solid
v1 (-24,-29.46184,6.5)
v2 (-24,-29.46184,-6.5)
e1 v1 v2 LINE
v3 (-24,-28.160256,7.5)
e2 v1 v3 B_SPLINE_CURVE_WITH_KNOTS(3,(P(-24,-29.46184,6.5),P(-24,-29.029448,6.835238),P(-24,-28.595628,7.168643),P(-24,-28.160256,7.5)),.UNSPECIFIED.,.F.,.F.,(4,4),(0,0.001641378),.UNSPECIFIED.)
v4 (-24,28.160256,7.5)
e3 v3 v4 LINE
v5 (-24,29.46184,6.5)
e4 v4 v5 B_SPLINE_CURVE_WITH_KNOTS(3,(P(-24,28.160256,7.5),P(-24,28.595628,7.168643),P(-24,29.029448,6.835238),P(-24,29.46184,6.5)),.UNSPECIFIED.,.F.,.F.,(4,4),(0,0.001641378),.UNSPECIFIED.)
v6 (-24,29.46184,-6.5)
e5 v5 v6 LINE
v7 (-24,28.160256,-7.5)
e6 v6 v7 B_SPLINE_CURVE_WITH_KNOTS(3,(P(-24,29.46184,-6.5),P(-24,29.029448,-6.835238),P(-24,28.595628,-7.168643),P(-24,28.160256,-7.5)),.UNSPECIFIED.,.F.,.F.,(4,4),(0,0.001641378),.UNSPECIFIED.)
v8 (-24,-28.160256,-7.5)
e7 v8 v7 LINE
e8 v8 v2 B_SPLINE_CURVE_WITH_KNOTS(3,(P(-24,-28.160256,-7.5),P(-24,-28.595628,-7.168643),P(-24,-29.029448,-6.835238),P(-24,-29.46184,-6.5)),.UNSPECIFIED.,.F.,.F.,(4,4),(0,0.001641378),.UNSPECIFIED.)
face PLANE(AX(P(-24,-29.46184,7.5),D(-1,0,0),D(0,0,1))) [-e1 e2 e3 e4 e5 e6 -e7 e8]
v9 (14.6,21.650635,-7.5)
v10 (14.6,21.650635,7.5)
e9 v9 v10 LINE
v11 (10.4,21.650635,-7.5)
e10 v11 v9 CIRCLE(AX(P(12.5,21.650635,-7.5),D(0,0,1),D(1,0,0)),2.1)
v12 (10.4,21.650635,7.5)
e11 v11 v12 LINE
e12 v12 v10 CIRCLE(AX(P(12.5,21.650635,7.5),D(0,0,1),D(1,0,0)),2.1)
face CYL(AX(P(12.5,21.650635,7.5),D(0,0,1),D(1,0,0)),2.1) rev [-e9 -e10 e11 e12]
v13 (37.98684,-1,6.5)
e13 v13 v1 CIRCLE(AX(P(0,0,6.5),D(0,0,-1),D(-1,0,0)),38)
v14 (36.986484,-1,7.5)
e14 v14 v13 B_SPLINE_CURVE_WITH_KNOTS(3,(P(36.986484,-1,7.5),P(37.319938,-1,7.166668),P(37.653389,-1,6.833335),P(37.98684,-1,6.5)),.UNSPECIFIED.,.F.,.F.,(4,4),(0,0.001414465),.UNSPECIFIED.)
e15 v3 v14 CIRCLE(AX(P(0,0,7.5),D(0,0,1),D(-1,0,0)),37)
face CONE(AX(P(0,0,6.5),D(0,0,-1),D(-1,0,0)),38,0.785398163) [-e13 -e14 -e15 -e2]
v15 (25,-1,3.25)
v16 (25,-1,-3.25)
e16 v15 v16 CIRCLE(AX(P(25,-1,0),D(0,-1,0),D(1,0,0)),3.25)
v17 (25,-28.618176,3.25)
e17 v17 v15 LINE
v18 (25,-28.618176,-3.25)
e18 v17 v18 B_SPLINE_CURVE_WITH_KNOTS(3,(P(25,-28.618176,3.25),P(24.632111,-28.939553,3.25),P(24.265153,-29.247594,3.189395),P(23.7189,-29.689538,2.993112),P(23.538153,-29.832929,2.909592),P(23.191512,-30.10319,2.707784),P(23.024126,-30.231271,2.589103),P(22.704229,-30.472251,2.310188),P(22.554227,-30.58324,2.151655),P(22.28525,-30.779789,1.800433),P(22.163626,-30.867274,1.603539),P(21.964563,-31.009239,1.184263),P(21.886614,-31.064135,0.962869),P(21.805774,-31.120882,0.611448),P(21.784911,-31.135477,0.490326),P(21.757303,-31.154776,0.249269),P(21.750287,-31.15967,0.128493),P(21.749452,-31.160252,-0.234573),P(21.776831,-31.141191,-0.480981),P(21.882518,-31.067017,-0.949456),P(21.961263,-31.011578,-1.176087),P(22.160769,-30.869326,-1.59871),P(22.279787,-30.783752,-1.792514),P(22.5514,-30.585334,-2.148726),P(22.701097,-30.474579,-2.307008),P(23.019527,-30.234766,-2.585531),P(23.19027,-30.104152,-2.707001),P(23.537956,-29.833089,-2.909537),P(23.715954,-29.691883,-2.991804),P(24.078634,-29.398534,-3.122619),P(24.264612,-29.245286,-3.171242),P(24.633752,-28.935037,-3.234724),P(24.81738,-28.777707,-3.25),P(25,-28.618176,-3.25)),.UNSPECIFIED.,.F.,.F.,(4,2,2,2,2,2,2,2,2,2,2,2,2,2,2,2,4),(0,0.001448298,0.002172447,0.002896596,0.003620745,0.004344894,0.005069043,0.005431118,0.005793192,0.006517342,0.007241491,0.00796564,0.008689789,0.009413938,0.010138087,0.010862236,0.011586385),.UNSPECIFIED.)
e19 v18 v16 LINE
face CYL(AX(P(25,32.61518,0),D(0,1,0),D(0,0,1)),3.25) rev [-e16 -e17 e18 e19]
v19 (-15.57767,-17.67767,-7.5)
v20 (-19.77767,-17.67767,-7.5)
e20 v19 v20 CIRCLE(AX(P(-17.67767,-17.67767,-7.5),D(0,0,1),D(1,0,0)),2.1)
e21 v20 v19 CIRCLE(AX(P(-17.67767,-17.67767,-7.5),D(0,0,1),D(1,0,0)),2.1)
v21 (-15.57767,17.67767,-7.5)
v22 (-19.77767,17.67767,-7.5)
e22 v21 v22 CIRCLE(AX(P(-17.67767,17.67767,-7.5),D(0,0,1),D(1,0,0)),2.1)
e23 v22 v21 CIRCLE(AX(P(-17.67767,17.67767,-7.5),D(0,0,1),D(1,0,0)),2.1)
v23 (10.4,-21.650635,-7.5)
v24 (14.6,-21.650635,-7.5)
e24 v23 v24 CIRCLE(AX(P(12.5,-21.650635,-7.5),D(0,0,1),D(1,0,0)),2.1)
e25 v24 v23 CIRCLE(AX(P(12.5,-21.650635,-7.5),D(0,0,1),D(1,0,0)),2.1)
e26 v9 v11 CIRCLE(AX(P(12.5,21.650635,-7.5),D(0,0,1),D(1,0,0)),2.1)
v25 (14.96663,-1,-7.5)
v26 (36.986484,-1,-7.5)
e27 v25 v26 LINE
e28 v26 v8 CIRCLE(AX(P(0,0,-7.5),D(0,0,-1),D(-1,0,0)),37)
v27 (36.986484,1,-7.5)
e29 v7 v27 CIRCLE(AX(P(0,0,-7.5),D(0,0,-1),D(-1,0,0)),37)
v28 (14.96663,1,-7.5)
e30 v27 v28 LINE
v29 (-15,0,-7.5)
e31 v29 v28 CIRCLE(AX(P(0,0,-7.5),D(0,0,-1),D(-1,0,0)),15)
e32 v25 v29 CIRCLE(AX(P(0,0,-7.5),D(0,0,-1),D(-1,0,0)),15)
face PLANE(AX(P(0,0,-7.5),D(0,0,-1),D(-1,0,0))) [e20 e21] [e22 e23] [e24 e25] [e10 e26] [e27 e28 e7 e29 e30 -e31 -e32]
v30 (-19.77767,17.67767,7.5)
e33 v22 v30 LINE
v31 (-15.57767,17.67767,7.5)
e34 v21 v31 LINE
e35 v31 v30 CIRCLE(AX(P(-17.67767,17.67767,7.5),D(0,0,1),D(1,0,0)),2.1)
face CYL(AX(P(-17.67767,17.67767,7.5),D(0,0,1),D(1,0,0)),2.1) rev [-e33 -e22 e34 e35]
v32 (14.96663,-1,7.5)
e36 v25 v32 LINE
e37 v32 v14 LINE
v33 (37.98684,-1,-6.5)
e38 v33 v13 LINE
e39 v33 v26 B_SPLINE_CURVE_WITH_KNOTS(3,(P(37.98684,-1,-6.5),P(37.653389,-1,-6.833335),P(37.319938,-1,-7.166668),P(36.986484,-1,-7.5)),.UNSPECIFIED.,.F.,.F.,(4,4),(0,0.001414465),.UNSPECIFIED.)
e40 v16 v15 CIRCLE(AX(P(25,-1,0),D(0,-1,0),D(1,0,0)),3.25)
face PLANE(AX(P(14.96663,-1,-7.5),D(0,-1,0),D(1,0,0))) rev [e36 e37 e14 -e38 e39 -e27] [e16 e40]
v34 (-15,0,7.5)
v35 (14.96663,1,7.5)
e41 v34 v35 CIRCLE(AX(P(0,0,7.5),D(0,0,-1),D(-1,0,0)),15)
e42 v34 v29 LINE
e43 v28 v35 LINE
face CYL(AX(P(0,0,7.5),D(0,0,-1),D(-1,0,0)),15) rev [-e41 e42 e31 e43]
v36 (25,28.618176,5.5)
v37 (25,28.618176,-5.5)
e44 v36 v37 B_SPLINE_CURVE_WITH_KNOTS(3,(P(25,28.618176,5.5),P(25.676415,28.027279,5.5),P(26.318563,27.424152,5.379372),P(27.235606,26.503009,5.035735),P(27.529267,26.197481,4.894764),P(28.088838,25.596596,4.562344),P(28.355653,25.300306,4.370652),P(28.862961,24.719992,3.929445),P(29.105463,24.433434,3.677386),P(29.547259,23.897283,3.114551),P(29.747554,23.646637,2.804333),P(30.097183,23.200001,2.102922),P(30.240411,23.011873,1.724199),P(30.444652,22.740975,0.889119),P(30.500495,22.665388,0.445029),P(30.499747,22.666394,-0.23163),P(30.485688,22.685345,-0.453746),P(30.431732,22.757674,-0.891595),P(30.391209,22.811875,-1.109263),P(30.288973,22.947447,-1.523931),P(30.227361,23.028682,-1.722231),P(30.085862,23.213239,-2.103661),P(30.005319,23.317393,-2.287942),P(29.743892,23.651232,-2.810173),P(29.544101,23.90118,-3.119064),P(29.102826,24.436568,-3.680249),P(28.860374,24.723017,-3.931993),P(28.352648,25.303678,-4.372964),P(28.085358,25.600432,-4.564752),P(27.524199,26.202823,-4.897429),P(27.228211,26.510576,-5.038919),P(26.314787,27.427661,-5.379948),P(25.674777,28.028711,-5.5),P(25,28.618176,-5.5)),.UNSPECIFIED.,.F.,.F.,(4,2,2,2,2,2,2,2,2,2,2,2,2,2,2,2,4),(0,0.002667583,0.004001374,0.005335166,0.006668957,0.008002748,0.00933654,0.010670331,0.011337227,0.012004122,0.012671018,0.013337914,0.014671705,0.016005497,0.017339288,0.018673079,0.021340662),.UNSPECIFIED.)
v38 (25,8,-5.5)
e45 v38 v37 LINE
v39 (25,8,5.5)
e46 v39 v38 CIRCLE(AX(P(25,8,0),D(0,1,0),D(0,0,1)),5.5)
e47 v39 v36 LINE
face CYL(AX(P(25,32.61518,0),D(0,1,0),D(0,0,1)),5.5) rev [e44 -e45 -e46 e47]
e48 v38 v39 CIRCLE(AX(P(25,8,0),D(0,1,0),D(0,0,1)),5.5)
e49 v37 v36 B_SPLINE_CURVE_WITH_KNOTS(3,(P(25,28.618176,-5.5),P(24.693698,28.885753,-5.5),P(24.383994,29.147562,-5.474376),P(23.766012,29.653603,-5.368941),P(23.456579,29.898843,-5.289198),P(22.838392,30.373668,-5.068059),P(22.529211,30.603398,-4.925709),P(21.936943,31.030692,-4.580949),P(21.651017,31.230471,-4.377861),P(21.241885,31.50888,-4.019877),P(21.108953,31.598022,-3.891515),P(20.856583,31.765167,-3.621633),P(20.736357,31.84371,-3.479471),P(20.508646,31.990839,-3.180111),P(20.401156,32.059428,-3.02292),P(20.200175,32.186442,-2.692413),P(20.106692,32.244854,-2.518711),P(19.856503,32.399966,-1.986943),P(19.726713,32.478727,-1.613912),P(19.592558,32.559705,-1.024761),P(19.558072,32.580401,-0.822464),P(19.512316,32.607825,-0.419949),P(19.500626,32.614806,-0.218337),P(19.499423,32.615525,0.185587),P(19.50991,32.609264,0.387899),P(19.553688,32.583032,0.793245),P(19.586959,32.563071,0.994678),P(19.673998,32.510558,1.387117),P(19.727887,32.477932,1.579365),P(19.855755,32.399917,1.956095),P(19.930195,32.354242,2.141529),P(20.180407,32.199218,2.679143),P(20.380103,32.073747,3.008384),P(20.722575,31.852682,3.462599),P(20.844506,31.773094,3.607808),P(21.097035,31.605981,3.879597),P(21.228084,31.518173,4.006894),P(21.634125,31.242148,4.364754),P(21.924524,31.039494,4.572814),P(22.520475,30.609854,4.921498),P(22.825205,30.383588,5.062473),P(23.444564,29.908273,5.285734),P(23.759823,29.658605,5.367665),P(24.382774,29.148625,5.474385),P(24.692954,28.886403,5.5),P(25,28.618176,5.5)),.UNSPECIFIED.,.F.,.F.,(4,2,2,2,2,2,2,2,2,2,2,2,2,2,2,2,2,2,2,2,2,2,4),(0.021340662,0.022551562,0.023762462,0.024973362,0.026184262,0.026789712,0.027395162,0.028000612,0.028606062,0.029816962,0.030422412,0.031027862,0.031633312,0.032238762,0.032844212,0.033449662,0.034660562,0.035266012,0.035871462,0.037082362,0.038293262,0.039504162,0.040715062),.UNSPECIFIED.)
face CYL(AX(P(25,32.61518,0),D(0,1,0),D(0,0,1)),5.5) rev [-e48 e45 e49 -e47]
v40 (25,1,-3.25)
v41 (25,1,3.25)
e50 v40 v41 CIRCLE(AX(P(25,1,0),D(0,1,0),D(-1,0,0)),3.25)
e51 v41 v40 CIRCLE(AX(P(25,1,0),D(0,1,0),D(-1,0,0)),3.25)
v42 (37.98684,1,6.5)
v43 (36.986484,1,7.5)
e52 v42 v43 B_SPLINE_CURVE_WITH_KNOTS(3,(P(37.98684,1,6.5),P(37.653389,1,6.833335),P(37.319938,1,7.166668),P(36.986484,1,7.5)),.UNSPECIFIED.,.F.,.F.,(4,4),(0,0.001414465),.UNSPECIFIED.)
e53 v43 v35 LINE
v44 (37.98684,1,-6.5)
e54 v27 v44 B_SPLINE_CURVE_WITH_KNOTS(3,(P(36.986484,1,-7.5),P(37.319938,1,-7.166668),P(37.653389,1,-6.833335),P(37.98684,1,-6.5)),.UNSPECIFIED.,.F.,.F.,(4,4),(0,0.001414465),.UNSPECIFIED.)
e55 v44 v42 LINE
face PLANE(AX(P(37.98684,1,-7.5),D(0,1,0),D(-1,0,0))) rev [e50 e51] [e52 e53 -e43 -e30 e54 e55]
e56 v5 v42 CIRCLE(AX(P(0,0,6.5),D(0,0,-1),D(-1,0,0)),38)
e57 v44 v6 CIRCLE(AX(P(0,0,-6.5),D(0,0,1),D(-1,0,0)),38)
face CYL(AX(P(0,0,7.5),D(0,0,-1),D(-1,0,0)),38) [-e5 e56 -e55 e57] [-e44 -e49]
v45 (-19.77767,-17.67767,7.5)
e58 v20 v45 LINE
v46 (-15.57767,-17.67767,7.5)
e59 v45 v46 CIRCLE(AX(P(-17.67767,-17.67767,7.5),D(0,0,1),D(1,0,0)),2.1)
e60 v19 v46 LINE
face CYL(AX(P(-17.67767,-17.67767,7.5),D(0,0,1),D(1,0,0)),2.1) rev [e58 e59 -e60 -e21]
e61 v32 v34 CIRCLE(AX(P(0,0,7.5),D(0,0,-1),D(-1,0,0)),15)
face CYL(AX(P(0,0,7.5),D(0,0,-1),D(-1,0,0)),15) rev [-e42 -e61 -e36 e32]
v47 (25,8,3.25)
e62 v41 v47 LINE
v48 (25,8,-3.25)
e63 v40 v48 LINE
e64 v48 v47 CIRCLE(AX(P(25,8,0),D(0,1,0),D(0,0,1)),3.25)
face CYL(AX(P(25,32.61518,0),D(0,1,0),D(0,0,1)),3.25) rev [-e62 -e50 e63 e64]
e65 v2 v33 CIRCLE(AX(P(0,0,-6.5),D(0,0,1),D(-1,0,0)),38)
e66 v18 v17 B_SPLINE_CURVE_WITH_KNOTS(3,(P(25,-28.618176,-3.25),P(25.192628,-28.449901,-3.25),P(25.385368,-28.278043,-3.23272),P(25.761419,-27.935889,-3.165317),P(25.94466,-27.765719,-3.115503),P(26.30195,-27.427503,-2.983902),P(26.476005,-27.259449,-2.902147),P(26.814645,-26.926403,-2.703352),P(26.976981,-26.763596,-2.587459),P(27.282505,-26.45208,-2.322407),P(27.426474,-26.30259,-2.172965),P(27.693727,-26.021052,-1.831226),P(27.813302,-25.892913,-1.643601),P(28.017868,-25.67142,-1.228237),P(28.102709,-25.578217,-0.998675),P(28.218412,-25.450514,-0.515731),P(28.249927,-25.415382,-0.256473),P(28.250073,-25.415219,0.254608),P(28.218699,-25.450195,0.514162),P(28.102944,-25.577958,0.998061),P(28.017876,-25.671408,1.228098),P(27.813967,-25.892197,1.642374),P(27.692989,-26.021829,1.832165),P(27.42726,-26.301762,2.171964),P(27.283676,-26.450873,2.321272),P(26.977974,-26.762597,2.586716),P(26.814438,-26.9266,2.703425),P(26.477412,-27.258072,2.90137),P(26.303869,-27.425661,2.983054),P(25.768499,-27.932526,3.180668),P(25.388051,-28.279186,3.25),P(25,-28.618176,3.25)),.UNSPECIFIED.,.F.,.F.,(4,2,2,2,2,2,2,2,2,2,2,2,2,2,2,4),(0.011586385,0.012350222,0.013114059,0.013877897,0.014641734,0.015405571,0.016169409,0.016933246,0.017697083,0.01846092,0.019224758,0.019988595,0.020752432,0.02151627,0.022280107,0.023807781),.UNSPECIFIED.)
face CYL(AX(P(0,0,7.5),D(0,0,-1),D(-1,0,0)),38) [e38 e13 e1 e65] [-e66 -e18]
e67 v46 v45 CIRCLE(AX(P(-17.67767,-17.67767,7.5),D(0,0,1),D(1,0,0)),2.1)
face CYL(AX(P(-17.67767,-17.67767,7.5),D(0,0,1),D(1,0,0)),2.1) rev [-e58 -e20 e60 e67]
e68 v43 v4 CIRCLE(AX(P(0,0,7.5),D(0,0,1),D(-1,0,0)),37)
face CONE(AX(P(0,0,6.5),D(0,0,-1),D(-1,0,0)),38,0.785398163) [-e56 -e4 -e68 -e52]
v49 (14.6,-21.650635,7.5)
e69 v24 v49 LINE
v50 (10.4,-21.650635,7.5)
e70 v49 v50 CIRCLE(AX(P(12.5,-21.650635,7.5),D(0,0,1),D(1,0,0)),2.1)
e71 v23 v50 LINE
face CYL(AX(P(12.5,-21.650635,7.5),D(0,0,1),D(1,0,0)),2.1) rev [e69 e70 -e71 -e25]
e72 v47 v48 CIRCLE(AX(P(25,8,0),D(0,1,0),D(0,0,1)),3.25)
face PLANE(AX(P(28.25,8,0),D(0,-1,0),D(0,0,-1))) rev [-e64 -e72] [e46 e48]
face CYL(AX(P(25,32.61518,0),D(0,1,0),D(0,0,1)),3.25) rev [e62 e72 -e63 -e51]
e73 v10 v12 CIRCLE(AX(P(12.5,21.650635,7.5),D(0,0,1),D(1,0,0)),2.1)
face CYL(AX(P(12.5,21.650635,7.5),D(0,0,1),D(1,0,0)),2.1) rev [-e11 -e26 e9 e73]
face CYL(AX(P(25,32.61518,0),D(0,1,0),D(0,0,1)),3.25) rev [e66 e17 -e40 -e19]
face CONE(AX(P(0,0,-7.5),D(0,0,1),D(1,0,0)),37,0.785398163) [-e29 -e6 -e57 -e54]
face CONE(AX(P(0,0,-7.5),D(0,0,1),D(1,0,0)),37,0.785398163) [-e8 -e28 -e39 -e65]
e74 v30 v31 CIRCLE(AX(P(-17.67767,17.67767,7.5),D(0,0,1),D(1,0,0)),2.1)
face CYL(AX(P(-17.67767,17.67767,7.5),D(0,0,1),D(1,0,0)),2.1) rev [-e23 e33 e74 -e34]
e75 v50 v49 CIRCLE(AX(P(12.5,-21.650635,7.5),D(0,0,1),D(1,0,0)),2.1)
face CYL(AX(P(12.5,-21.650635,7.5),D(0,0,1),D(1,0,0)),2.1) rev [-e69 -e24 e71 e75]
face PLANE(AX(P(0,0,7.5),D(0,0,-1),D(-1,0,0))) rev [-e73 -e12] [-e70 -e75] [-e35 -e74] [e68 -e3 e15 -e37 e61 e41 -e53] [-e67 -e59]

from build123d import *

# Parameters (mm, degrees)
EXTRUDE_1_DEPTH              = 15
CUT_EXTRUDE_1_DEPTH          = 56.794264938
SKETCH_3_W                   = 15
SKETCH_3_H                   = 15
HOLE_WIZARD_4_2_4_2_1_D      = 4.2
SKETCH_6_W                   = 2.5
SKETCH_6_H                   = 37
HOLE_WIZARD_M6_1_D           = 6.5
HOLE_WIZARD_M6_1_DEPTH       = 70.615180295
HOLE_WIZARD_M6_1_CBORE_D     = 11
HOLE_WIZARD_M6_1_CBORE_DEPTH = 24.615180295
CHAMFER_1_SIZE               = 1


with BuildPart() as part:
    # 草图1 → 凸台-拉伸1 (new body)
    with BuildSketch(Plane(origin=(0, 0, -7.5), x_dir=(-1, 0, 0), z_dir=(0, 0, -1))):
        with BuildLine():
            Line((24, -29.461839725), (24, 29.461839725))
            ThreePointArc((24, 29.461839725), (-38, 0), (24, -29.461839725))
        make_face()
    extrude(amount=-EXTRUDE_1_DEPTH)

    # 草图2 → 切除-拉伸1 (cut, through all)
    with BuildSketch(Plane.XY.offset(7.5)):
        with BuildLine():
            Line((37.986839826, 1), (14.966629547, 1))
            ThreePointArc((14.966629547, 1), (15, 0), (14.966629547, -1))
            Line((14.966629547, -1), (37.986839826, -1))
            ThreePointArc((37.986839826, -1), (38, 0), (37.986839826, 1))
        make_face()
    extrude(amount=-CUT_EXTRUDE_1_DEPTH, mode=Mode.SUBTRACT)

    # 草图3 → 切除-旋转1 (revolve, cut)
    with BuildSketch(Plane.XZ):
        with Locations((7.5, 0)):
            Rectangle(SKETCH_3_W, SKETCH_3_H)
    revolve(axis=Axis((0, 0, 7.5), (0, 0, -1)), mode=Mode.SUBTRACT)

    # Ø4.2 (4.2) 直径孔1 (through all)
    with Locations(Plane.XY.offset(7.5)):
        with Locations((-17.67766953, -17.67766953), (-17.67766953, 17.67766953), (12.5, 21.650635095), (12.5, -21.650635095)):
            Hole(HOLE_WIZARD_4_2_4_2_1_D / 2)

    # 草图6 → Ø5.0 (5) 直径孔1 (revolve, cut)
    with BuildSketch(Plane(origin=(25, -1, 0), x_dir=(0, 0, 1), z_dir=(1, 0, 0))):
        with Locations((1.25, 18.5)):
            Rectangle(SKETCH_6_W, SKETCH_6_H)
    revolve(axis=Axis((25, 5.35, 0), (0, -1, 0)), mode=Mode.SUBTRACT)

    # M6 六角头螺栓的柱形沉头孔1
    with Locations(Plane(origin=(0, 32.615180295, 0), x_dir=(1, 0, 0), z_dir=(0, 1, 0))):
        with Locations((25, 0)):
            CounterBoreHole(HOLE_WIZARD_M6_1_D / 2, HOLE_WIZARD_M6_1_CBORE_D / 2, HOLE_WIZARD_M6_1_CBORE_DEPTH, depth=HOLE_WIZARD_M6_1_DEPTH)

    # 倒角1
    chamfer_1_edges = [part.edges().sort_by_distance(p)[0] for p in [
        (15.856449862, -34.533650224, 7.5),
        (15.856449862, 34.533650224, -7.5),
        (15.856449862, 34.533650224, 7.5),
        (15.856449862, -34.533650224, -7.5),
    ]]
    chamfer(chamfer_1_edges, length=CHAMFER_1_SIZE)


solid = part.part
